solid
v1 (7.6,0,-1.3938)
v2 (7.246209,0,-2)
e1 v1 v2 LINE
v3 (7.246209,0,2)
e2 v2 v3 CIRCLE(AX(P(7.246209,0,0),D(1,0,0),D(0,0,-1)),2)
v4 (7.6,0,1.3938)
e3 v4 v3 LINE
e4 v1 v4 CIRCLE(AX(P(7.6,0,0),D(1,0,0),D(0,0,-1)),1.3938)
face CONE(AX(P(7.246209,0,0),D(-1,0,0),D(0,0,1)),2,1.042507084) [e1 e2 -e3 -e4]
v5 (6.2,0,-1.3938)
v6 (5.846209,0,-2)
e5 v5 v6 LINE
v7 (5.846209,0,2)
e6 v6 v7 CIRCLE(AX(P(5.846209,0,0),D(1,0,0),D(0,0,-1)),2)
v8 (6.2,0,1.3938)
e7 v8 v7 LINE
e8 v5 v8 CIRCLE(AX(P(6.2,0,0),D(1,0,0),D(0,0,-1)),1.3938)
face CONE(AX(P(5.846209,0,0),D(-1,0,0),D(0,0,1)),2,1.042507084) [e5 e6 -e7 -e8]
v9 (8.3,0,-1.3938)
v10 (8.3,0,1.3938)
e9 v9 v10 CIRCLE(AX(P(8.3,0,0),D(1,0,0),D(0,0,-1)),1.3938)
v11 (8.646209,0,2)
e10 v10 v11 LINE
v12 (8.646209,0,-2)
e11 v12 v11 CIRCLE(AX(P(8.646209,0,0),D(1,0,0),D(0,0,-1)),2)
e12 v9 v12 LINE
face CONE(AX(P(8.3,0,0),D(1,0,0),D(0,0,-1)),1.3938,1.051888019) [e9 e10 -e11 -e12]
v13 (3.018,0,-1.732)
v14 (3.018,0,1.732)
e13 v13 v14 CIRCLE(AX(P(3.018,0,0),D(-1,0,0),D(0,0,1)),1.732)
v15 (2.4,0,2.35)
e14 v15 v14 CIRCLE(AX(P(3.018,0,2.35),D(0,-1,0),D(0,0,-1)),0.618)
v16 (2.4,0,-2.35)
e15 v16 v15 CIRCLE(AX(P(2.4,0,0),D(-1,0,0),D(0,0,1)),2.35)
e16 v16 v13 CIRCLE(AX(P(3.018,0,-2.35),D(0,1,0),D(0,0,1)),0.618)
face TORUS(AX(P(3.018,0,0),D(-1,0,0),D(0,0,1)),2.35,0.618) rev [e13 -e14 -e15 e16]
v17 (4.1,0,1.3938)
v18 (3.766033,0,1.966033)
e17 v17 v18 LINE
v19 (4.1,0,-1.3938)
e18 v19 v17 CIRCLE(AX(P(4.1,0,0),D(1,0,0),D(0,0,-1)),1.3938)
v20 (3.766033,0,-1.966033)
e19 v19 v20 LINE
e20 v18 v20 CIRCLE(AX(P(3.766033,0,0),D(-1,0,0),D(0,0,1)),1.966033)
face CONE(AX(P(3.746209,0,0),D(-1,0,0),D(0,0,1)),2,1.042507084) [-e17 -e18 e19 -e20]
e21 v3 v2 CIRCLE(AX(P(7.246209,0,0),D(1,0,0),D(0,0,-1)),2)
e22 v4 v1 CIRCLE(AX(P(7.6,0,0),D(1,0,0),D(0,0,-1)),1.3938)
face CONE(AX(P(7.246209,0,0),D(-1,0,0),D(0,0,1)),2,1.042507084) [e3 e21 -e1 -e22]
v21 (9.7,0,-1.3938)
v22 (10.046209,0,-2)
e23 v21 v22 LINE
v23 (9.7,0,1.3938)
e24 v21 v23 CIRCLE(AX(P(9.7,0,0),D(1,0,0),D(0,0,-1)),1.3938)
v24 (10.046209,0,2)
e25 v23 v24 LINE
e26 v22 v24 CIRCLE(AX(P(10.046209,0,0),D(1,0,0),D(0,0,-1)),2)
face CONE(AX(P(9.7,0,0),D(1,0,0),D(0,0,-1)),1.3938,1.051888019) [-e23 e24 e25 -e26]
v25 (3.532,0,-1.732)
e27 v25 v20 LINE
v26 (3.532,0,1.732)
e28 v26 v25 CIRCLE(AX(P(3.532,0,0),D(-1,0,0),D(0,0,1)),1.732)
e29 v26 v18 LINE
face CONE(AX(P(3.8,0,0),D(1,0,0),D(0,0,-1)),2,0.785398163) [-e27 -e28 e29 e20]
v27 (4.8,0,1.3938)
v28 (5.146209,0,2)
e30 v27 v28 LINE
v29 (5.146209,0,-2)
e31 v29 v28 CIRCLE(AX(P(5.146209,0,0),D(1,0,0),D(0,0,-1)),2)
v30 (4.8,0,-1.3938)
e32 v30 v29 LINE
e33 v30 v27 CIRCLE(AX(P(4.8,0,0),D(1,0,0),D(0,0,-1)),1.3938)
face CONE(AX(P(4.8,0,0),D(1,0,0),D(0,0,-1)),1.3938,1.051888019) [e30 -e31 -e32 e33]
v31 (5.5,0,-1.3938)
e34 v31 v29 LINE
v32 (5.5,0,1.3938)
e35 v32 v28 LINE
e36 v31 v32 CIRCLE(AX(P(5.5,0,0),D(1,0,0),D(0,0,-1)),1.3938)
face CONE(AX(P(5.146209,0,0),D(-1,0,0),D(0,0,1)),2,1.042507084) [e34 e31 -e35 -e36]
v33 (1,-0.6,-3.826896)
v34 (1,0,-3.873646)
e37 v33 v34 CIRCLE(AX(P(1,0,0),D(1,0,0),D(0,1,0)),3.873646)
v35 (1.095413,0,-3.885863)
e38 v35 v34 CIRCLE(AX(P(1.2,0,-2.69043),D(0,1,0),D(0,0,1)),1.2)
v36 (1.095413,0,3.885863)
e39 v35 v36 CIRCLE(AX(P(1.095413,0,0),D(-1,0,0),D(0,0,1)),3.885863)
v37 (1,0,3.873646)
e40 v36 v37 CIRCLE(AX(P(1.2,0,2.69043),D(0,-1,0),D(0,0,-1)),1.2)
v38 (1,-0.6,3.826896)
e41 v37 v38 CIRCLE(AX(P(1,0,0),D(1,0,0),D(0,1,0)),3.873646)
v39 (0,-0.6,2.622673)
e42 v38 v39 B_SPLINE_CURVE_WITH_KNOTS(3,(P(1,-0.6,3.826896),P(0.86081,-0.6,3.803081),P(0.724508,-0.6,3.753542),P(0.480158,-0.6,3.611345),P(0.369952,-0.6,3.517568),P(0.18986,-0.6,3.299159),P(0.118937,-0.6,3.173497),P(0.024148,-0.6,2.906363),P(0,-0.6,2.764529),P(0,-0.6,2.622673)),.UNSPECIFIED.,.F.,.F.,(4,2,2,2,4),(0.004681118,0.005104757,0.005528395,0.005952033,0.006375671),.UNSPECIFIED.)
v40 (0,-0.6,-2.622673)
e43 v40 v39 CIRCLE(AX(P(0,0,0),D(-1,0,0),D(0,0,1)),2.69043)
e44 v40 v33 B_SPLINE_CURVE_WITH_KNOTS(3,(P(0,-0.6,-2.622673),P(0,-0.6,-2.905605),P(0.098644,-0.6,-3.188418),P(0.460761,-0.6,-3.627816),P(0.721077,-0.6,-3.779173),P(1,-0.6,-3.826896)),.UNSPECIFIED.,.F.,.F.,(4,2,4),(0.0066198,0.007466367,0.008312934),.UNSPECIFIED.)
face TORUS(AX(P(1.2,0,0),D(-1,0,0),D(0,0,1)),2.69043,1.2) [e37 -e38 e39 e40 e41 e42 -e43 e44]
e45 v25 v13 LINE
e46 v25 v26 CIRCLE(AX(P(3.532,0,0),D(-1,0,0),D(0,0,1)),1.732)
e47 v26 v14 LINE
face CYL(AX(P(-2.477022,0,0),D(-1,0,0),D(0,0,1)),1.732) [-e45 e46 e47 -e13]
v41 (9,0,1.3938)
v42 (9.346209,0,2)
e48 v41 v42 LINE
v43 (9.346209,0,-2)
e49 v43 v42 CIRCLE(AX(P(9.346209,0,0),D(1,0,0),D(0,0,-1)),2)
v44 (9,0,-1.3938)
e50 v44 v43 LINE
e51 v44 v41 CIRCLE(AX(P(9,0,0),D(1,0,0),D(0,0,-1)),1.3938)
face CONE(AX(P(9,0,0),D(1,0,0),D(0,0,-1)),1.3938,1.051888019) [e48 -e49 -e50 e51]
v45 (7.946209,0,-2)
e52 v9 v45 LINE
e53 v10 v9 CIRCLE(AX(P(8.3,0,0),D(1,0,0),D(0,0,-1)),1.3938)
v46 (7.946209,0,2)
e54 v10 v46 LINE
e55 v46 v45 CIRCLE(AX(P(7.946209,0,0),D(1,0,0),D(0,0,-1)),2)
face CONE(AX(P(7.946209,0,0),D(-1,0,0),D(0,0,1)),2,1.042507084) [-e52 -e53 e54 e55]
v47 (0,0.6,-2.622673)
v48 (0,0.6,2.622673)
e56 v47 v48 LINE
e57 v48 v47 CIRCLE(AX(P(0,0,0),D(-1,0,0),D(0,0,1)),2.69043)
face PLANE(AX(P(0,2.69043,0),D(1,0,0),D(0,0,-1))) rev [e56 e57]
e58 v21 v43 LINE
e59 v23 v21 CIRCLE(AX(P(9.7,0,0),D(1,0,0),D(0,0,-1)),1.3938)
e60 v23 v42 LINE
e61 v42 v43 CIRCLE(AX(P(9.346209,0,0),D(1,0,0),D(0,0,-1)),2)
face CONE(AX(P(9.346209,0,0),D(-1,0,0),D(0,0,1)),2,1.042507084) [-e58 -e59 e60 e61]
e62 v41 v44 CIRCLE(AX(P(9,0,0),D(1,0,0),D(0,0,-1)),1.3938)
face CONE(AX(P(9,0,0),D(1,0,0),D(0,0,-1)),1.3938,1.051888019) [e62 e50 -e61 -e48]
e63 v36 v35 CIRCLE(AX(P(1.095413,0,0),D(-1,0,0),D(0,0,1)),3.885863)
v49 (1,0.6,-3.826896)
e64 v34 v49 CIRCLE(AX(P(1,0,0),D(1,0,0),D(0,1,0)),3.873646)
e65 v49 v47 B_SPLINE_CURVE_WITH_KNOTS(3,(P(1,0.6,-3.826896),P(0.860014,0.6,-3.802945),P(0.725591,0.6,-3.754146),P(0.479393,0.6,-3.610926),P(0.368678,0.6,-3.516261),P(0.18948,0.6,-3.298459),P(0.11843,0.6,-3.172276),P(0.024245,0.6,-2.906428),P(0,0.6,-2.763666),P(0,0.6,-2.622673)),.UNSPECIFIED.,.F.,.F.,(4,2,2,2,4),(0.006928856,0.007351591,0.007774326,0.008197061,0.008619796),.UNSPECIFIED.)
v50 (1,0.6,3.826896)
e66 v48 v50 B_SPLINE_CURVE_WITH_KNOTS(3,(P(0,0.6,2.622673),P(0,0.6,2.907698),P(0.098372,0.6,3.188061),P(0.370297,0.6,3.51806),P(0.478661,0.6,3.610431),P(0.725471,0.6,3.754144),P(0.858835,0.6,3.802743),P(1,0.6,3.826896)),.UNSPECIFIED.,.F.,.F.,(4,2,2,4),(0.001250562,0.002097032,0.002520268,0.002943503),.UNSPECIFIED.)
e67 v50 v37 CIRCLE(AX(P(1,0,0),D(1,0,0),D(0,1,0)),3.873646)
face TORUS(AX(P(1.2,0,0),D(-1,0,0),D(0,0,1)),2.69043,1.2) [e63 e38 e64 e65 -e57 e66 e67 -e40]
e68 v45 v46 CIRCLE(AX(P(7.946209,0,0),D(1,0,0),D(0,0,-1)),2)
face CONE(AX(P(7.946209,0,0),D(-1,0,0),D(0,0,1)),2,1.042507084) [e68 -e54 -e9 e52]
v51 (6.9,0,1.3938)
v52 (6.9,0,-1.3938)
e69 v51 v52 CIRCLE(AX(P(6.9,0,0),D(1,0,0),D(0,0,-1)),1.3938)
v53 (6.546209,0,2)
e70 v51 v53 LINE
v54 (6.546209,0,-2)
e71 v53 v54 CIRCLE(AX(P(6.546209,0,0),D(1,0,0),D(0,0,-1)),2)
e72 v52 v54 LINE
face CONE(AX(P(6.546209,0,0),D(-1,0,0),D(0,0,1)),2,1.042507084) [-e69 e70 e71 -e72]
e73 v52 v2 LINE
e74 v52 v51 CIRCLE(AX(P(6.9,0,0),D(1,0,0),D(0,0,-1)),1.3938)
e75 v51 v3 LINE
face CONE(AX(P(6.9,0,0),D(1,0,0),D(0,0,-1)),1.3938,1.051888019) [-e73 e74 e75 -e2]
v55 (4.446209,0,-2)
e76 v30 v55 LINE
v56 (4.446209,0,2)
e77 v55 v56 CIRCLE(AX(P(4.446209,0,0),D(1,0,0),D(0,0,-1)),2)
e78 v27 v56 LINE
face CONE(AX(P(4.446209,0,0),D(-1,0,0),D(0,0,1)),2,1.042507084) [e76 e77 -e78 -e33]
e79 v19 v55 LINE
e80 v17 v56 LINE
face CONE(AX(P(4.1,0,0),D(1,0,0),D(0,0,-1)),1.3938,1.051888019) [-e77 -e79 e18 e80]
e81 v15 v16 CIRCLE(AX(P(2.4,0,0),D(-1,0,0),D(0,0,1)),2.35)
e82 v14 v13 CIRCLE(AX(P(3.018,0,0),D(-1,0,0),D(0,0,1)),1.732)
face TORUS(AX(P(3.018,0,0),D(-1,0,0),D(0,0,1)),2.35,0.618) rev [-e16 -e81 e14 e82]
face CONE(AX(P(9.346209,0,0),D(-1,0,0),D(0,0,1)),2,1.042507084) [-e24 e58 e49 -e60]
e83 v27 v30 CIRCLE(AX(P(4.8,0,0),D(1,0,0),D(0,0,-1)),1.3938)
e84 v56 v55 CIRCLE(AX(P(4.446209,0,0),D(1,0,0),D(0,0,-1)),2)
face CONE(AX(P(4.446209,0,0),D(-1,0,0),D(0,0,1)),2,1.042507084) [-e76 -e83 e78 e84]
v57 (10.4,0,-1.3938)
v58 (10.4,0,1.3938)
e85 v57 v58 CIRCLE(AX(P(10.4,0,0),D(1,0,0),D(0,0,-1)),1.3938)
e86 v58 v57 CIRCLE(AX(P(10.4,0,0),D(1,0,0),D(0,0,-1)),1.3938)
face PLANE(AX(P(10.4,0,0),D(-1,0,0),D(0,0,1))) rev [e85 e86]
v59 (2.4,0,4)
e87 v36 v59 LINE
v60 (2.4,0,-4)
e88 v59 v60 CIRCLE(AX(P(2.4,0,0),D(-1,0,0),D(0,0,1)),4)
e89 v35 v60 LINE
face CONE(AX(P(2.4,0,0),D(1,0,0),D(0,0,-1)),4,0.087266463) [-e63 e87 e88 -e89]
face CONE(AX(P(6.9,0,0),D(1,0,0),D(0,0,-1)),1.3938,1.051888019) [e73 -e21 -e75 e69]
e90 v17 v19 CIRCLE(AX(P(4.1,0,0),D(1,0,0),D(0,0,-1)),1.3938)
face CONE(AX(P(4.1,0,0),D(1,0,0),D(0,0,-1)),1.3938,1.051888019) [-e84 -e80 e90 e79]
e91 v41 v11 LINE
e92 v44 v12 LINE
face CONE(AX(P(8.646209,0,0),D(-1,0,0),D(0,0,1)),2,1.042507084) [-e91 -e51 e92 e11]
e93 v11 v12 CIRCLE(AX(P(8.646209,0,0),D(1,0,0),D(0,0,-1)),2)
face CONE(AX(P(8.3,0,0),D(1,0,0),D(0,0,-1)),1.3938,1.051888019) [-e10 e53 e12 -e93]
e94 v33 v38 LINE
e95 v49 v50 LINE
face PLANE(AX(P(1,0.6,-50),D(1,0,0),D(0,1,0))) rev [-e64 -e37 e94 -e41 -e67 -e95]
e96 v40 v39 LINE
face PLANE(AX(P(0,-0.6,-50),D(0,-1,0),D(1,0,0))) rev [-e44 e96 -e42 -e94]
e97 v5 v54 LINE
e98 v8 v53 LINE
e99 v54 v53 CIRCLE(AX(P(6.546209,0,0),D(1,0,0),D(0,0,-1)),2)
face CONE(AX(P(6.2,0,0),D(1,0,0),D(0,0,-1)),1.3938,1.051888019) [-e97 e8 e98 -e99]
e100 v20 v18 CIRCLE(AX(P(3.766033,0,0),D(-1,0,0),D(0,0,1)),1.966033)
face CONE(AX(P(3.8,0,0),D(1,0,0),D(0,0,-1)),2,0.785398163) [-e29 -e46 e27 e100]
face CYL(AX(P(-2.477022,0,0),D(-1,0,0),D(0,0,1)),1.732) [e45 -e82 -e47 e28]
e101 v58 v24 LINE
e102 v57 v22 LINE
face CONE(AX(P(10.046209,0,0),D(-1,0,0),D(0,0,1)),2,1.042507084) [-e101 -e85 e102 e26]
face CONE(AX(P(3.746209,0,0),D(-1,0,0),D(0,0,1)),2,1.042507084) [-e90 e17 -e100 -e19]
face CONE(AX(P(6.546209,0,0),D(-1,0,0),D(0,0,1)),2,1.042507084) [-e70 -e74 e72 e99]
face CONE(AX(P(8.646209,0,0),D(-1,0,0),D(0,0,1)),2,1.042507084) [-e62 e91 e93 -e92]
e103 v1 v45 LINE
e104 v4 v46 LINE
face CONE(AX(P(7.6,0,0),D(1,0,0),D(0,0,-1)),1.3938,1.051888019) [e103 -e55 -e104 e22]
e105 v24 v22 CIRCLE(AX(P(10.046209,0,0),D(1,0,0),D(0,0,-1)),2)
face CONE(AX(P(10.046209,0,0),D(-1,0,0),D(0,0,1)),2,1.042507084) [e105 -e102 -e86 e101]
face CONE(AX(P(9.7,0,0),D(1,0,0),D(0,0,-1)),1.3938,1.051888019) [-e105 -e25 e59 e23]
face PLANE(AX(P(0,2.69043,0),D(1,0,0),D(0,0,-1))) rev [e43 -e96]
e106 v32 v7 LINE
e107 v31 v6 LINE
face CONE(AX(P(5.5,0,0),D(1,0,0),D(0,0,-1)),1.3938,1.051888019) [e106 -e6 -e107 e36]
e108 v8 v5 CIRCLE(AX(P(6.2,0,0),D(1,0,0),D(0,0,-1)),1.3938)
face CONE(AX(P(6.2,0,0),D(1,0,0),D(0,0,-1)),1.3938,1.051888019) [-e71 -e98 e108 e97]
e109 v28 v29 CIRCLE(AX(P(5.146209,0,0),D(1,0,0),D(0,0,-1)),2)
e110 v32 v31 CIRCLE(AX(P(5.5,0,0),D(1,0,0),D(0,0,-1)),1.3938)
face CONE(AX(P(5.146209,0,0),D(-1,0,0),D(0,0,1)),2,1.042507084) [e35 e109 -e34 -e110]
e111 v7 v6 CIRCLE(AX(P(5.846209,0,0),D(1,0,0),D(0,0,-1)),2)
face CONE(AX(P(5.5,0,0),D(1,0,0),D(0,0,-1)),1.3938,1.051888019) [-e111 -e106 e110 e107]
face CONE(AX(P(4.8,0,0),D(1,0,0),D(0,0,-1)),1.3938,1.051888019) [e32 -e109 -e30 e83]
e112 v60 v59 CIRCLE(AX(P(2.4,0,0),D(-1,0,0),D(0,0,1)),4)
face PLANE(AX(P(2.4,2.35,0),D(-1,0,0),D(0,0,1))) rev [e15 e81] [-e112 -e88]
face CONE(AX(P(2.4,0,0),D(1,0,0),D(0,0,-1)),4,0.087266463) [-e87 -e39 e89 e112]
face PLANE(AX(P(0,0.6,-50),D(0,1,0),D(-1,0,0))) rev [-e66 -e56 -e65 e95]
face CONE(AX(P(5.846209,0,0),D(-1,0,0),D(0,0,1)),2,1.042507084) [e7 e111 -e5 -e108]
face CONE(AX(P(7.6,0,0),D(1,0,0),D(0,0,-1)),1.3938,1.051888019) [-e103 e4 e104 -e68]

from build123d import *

# Parameters (mm, degrees)
SKETCH_4_W             = 1
SKETCH_4_H             = 1.2
CUT_EXTRUDE_1_DEPTH    = 50
PATTERN_LINEAR_1_COUNT = 10
PATTERN_LINEAR_1_PITCH = 0.7


with BuildPart() as part:
    # 草图3 → Revolve 915 (revolve)
    with BuildSketch(Plane.XY, mode=Mode.PRIVATE) as revolve_915_sk:
        with BuildLine():
            Line((0, 0), (10.4, 0))
            Line((10.4, 0), (10.4, 2))
            Line((10.4, 2), (3.8, 2))
            Line((3.8, 2), (3.532, 1.732))
            Line((3.532, 1.732), (3.018, 1.732))
            ThreePointArc((3.018, 1.732), (2.581008009, 1.913008009), (2.4, 2.35))
            Line((2.4, 2.35), (2.4, 4))
            Line((2.4, 4), (1.095413109, 3.885863436))
            ThreePointArc((1.095413109, 3.885863436), (0.315267196, 3.501138048), (0, 2.690429799))
            Line((0, 2.690429799), (0, 0))
        make_face()
    revolve(revolve_915_sk.sketch.rotate(Axis((-2.477021524, 0, 0), (1, 0, 0)), 90), axis=Axis((-2.477021524, 0, 0), (1, 0, 0)))

    # 草图4 → 切除-拉伸1 (cut, symmetric)
    with BuildSketch(Plane.XY):
        with Locations((0.5, 0)):
            Rectangle(SKETCH_4_W, SKETCH_4_H)
    extrude(amount=CUT_EXTRUDE_1_DEPTH, both=True, mode=Mode.SUBTRACT)

    # 草图5 → 切除-旋转1 (revolve, cut)
    with BuildSketch(Plane.XY, mode=Mode.PRIVATE) as cut_revolve_1_sk:
        Polygon((10.046208796, 2), (10.746208796, 2), (10.4, 1.3938), align=None)
    cut_revolve_1 = revolve(cut_revolve_1_sk.sketch.rotate(Axis((6.174994867, 0, 0), (-1, 0, 0)), 270), axis=Axis((6.174994867, 0, 0), (-1, 0, 0)), mode=Mode.SUBTRACT)

    # 阵列(线性)1: 切除-旋转1 ×10
    with Locations(*[(-i * PATTERN_LINEAR_1_PITCH, 0, 0) for i in range(1, PATTERN_LINEAR_1_COUNT)]):
        add(cut_revolve_1, mode=Mode.SUBTRACT)


solid = part.part
